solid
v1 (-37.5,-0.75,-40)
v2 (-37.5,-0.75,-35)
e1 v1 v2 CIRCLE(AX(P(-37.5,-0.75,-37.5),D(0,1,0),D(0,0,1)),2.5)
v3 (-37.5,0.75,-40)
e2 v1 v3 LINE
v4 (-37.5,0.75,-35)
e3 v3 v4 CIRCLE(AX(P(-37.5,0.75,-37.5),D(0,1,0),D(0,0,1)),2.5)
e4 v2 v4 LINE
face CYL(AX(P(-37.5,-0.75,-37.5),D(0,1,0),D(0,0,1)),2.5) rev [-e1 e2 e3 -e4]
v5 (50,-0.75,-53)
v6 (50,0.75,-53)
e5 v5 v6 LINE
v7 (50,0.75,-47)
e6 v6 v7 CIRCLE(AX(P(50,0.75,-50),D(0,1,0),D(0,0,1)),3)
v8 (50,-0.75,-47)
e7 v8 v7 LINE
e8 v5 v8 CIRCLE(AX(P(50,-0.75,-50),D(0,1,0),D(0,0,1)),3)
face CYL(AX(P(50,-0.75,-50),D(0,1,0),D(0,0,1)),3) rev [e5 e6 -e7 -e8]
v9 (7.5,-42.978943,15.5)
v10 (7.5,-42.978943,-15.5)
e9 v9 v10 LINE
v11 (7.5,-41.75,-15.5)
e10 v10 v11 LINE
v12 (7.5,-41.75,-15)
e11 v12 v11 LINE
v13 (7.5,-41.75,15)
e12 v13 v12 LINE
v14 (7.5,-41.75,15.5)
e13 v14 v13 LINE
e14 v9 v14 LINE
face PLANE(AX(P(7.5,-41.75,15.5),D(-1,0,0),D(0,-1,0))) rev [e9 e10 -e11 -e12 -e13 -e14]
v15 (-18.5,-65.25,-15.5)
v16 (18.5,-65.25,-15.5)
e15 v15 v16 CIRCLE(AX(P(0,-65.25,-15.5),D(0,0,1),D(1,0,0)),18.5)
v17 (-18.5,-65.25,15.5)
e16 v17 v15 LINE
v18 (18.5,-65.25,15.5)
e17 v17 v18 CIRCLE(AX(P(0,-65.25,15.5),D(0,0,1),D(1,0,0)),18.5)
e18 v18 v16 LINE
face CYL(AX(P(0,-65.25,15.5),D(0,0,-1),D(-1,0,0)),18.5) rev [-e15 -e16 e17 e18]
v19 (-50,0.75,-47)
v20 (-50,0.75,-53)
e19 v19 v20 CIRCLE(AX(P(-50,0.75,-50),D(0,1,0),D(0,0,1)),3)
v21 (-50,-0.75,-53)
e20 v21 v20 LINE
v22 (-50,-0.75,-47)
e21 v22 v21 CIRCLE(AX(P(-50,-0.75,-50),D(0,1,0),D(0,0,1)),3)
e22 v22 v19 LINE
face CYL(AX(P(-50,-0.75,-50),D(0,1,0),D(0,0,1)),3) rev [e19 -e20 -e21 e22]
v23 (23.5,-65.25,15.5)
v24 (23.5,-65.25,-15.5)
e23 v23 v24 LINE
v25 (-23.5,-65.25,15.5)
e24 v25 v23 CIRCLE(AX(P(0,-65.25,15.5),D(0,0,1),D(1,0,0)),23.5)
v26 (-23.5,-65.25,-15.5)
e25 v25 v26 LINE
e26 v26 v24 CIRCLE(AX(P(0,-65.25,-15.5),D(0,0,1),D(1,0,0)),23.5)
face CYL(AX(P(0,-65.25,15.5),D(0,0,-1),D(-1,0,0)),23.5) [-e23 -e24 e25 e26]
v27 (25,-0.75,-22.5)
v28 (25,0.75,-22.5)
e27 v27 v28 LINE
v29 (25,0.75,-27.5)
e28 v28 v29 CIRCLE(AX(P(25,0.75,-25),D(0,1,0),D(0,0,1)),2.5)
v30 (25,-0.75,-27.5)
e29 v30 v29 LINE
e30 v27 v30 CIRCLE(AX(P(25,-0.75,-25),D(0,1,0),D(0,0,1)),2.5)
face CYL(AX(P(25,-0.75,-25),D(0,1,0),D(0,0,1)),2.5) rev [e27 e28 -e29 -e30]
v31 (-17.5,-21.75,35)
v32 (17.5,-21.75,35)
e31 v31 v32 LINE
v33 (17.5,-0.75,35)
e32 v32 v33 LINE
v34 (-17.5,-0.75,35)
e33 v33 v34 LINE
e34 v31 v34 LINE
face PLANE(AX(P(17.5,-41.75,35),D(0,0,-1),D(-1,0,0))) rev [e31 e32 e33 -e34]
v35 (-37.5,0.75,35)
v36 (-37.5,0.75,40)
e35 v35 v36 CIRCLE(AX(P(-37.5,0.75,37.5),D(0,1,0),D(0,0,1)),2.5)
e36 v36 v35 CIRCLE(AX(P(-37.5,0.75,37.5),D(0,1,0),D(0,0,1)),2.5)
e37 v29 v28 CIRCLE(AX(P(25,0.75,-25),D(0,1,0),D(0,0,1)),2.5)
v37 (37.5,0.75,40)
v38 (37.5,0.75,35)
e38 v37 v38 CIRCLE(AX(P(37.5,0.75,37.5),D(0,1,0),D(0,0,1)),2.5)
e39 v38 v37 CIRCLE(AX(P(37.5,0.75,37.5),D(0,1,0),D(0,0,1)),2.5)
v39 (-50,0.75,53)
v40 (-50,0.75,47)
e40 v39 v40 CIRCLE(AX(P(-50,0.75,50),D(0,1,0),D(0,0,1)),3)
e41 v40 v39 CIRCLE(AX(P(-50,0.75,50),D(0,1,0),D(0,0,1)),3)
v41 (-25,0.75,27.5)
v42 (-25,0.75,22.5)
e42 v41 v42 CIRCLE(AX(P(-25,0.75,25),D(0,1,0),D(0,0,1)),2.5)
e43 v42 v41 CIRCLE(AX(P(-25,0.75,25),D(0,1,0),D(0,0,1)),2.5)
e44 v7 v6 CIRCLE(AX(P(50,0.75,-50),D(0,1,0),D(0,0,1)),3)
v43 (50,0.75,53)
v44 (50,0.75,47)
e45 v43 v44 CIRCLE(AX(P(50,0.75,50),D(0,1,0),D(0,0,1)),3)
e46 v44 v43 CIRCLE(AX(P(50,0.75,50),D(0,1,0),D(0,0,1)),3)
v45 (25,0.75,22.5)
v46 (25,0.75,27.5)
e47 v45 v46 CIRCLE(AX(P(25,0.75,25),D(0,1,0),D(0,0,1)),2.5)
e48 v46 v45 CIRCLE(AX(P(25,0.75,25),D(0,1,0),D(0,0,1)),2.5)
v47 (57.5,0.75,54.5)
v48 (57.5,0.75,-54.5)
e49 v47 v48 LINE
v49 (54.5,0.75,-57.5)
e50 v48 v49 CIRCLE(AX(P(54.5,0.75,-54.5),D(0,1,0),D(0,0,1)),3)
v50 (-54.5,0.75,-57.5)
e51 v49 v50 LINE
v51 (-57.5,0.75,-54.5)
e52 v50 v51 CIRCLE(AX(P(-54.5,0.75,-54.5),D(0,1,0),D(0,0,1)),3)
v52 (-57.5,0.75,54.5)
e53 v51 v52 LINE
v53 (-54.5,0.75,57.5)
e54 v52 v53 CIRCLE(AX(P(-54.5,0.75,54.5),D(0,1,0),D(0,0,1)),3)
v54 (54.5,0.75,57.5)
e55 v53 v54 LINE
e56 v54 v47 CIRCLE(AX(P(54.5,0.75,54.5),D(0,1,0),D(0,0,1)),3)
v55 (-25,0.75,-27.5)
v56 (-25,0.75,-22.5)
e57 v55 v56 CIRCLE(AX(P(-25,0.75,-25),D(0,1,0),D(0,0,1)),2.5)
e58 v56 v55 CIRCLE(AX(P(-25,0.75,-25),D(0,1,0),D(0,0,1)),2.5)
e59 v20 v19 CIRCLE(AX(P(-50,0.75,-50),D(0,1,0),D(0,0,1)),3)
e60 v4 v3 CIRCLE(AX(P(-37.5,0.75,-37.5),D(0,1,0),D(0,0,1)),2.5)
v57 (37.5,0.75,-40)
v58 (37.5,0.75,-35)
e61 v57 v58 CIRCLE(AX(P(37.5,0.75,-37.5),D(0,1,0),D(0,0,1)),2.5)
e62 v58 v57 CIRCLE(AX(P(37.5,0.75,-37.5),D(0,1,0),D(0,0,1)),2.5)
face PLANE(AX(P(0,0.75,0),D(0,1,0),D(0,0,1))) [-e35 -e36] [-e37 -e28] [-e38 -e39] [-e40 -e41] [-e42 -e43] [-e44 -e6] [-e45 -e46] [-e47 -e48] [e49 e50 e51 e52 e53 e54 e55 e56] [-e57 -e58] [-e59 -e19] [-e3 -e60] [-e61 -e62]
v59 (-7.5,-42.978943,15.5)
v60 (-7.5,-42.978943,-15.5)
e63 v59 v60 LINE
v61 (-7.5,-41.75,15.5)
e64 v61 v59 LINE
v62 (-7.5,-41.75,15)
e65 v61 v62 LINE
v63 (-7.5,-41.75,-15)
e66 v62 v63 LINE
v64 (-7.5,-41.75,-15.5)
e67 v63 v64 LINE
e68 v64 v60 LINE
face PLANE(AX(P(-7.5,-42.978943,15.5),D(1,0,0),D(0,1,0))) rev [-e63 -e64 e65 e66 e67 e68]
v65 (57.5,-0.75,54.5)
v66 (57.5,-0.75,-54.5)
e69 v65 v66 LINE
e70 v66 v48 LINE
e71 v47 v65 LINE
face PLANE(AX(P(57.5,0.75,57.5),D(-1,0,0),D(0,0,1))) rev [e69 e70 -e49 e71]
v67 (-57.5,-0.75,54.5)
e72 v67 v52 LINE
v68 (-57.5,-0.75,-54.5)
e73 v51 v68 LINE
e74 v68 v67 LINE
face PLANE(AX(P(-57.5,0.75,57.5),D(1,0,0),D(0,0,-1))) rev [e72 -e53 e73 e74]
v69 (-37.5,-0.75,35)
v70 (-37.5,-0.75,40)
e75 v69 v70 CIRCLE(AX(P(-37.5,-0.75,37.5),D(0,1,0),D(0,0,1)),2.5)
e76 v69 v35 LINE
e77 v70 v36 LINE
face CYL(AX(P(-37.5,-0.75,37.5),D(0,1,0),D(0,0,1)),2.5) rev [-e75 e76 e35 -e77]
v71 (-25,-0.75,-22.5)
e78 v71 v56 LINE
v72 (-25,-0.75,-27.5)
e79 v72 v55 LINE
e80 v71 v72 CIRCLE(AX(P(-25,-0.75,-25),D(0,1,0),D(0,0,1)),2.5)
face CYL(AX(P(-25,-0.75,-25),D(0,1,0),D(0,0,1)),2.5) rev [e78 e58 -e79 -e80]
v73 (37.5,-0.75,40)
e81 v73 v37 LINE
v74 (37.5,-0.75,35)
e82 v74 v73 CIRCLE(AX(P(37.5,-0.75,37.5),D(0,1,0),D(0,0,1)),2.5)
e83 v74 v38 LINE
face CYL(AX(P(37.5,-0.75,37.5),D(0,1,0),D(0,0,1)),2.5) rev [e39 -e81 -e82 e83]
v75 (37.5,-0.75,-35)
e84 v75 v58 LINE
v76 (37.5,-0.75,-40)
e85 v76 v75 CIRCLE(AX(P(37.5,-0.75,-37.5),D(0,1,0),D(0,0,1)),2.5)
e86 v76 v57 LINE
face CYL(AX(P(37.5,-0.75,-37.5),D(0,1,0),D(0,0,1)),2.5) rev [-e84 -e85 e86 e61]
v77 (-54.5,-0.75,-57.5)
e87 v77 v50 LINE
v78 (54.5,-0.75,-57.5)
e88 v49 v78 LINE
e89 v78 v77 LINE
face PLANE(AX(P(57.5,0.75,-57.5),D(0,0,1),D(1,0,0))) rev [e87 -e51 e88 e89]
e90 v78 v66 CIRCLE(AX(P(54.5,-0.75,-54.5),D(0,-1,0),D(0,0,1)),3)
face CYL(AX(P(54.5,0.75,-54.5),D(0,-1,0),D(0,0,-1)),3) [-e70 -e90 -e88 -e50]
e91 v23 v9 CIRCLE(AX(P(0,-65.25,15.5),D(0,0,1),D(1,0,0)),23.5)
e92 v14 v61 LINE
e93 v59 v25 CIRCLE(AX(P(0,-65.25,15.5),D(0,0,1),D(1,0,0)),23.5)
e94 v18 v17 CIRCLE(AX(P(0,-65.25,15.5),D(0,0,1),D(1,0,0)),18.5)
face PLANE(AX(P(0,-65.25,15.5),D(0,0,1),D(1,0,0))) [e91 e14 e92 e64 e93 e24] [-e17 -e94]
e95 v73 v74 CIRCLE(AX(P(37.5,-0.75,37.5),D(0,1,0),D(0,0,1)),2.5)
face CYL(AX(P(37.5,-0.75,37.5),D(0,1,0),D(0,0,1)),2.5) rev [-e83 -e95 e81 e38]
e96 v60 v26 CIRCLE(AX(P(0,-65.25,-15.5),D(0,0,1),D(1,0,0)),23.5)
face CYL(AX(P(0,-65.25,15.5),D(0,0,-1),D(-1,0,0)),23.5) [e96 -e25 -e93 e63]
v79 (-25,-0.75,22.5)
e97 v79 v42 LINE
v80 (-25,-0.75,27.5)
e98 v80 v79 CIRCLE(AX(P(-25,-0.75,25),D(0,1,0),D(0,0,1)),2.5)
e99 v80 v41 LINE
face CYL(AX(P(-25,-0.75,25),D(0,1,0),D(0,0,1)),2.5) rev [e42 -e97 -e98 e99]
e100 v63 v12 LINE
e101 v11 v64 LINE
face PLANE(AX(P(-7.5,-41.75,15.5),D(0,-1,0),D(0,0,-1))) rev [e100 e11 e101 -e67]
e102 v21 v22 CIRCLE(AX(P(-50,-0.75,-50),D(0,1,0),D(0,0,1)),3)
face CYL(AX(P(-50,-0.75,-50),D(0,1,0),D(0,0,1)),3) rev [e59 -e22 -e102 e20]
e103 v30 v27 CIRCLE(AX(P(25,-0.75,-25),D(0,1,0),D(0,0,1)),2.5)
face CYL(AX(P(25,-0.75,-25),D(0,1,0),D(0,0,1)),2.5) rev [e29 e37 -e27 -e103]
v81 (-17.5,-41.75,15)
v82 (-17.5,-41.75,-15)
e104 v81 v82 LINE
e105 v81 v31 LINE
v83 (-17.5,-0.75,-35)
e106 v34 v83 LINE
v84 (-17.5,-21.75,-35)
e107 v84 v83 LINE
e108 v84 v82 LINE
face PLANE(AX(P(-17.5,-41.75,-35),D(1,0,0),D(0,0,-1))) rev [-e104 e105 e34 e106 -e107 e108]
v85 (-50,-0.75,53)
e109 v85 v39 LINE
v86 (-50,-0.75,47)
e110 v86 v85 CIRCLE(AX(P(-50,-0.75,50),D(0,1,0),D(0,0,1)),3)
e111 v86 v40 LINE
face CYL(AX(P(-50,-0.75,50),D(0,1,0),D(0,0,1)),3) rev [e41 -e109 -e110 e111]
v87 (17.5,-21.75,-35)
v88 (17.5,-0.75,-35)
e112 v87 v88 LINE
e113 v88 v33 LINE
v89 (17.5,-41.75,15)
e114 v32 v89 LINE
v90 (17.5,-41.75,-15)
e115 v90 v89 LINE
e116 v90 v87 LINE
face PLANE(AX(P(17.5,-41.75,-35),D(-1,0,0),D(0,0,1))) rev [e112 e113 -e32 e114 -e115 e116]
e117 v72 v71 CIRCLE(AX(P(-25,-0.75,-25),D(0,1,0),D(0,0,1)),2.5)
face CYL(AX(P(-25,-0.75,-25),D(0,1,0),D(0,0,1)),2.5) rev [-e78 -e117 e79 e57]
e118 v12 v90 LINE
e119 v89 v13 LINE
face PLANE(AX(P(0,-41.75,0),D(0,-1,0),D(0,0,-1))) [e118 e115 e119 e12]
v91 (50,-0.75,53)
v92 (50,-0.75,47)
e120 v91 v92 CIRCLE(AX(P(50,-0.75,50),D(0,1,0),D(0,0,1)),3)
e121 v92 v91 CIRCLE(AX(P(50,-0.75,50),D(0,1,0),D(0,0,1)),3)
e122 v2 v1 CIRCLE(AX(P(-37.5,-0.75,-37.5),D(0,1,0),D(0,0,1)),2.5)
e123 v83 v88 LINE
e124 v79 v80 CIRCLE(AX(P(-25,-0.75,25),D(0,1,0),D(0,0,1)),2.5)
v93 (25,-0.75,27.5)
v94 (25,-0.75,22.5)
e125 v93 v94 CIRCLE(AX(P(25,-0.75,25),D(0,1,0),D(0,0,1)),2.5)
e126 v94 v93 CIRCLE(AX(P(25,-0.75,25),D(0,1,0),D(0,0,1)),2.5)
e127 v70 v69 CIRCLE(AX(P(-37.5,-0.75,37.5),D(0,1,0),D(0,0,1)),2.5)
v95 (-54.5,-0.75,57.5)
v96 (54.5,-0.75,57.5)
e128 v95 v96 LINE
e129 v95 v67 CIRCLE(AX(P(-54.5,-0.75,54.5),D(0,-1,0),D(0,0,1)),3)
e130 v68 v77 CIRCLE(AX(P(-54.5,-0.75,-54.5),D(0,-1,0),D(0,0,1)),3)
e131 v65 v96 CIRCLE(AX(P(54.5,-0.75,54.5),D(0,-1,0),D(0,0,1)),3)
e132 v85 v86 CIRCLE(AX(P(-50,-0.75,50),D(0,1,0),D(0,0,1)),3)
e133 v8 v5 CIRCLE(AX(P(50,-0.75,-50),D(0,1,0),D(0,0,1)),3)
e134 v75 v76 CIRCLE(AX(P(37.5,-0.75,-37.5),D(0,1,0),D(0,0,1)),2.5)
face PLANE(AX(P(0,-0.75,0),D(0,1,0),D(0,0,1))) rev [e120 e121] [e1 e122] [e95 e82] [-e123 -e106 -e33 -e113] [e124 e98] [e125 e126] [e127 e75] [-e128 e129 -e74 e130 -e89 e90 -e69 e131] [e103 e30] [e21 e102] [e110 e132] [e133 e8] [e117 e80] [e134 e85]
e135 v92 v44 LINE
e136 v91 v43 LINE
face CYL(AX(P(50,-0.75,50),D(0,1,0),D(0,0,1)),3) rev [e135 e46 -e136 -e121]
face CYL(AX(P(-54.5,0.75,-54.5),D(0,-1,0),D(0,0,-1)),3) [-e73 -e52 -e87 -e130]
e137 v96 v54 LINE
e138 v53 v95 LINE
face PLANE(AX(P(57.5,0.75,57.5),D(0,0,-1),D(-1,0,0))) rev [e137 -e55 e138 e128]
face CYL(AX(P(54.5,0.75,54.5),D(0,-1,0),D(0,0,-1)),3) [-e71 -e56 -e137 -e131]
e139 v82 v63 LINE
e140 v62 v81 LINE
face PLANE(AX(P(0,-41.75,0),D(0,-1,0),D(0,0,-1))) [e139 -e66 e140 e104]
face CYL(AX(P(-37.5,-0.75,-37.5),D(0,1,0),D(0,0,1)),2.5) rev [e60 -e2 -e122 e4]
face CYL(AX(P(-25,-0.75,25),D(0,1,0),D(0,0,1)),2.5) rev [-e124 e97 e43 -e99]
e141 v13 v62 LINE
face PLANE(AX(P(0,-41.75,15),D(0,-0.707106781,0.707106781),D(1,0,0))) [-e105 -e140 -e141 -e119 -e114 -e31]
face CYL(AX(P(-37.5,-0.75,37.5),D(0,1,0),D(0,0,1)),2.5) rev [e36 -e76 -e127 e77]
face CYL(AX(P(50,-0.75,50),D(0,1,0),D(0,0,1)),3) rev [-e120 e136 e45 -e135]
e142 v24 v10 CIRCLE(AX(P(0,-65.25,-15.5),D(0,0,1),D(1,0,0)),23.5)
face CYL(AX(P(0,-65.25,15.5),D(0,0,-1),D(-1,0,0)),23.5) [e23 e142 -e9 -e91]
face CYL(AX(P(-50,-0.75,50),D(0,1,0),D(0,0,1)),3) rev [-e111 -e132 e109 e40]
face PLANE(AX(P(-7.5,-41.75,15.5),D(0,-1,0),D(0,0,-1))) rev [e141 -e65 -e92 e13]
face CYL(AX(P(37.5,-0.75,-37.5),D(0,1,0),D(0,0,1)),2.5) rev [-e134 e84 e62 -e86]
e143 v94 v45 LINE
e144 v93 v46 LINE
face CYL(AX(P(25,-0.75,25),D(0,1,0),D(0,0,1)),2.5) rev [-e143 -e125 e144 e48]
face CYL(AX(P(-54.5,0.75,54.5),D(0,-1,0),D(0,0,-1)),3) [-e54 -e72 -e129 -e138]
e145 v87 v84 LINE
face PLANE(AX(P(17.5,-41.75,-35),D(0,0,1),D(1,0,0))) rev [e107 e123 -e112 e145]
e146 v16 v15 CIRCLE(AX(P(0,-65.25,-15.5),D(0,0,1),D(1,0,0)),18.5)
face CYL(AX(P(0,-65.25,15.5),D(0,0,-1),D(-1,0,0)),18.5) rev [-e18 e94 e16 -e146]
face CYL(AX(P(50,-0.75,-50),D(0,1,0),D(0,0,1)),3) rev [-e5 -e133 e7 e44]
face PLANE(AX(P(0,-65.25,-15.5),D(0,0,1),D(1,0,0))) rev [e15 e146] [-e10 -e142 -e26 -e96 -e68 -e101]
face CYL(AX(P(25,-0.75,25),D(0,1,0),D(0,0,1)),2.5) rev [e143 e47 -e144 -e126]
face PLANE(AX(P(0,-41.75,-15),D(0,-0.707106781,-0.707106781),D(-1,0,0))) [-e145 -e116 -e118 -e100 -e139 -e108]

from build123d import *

# Parameters (mm, degrees)
SKETCH_1_W          = 115
SKETCH_1_H          = 115
EXTRUDE_1_DEPTH     = 0.75
SKETCH_2_R          = 2.5
CUT_EXTRUDE_1_DEPTH = 82.331113358
SKETCH_3_R          = 2.5
CUT_EXTRUDE_2_DEPTH = 82.331113358
SKETCH_4_R          = 3
CUT_EXTRUDE_3_DEPTH = 82.331113358
FILLET_1_R          = 3
SKETCH_5_W          = 35
SKETCH_5_H          = 70
EXTRUDE_2_DEPTH     = 41
CHAMFER_1_SIZE      = 20
SKETCH_6_R          = 18.5
EXTRUDE_3_DEPTH     = 15.5


with BuildPart() as part:
    # 草图1 → 凸台-拉伸1 (new, symmetric)
    with BuildSketch(Plane(origin=(0, 0, 0), x_dir=(1, 0, 0), z_dir=(0, 1, 0))):
        Rectangle(SKETCH_1_W, SKETCH_1_H)
    extrude(amount=EXTRUDE_1_DEPTH, both=True)

    # 草图2 → 切除-拉伸1 (cut, through all)
    with BuildSketch(Plane(origin=(0, 0.75, 0), x_dir=(1, 0, 0), z_dir=(0, 1, 0))):
        with Locations(Location((-25, 25, 0), (0, 0, 270))):
            Circle(SKETCH_2_R)
        with Locations(Location((25, 25, 0), (0, 0, 270))):
            Circle(SKETCH_2_R)
        with Locations(Location((25, -25, 0), (0, 0, 270))):
            Circle(SKETCH_2_R)
        with Locations(Location((-25, -25, 0), (0, 0, 270))):
            Circle(SKETCH_2_R)
    extrude(amount=-CUT_EXTRUDE_1_DEPTH, mode=Mode.SUBTRACT)

    # 草图3 → 切除-拉伸2 (cut, through all)
    with BuildSketch(Plane(origin=(0, 0.75, 0), x_dir=(1, 0, 0), z_dir=(0, 1, 0))):
        with Locations(Location((-37.5, 37.5, 0), (0, 0, 270))):
            Circle(SKETCH_3_R)
        with Locations(Location((-37.5, -37.5, 0), (0, 0, 270))):
            Circle(SKETCH_3_R)
        with Locations(Location((37.5, -37.5, 0), (0, 0, 270))):
            Circle(SKETCH_3_R)
        with Locations(Location((37.5, 37.5, 0), (0, 0, 270))):
            Circle(SKETCH_3_R)
    extrude(amount=-CUT_EXTRUDE_2_DEPTH, mode=Mode.SUBTRACT)

    # 草图4 → 切除-拉伸3 (cut, through all)
    with BuildSketch(Plane(origin=(0, 0.75, 0), x_dir=(1, 0, 0), z_dir=(0, 1, 0))):
        with Locations(Location((-50, 50, 0), (0, 0, 270))):
            Circle(SKETCH_4_R)
        with Locations(Location((50, 50, 0), (0, 0, 270))):
            Circle(SKETCH_4_R)
        with Locations(Location((-50, -50, 0), (0, 0, 270))):
            Circle(SKETCH_4_R)
        with Locations(Location((50, -50, 0), (0, 0, 270))):
            Circle(SKETCH_4_R)
    extrude(amount=-CUT_EXTRUDE_3_DEPTH, mode=Mode.SUBTRACT)

    # 圆角1
    fillet_1_edges = [part.edges().sort_by_distance(p)[0] for p in [
        (-57.5, 0, -57.5),
        (57.5, 0, -57.5),
        (57.5, 0, 57.5),
        (-57.5, 0, 57.5),
    ]]
    fillet(fillet_1_edges, radius=FILLET_1_R)

    # 草图5 → 凸台-拉伸2 (add)
    with BuildSketch(Plane.XZ.offset(0.75)):
        Rectangle(SKETCH_5_W, SKETCH_5_H)
    extrude(amount=EXTRUDE_2_DEPTH)

    # 倒角1
    chamfer_1_edges = [part.edges().sort_by_distance(p)[0] for p in [
        (0, -41.75, -35),
        (0, -41.75, 35),
    ]]
    chamfer(chamfer_1_edges, length=CHAMFER_1_SIZE)

    # 草图6 → 凸台-拉伸3 (add, symmetric)
    with BuildSketch(Plane.XY):
        with BuildLine():
            Line((7.5, -41.75), (7.5, -42.978942549))
            ThreePointArc((7.5, -42.978942549), (0, -88.75), (-7.5, -42.978942549))
            Line((-7.5, -42.978942549), (-7.5, -41.75))
            Line((-7.5, -41.75), (7.5, -41.75))
        make_face()
        with Locations((0, -65.25)):
            Circle(SKETCH_6_R, mode=Mode.SUBTRACT)
    extrude(amount=EXTRUDE_3_DEPTH, both=True)


solid = part.part
